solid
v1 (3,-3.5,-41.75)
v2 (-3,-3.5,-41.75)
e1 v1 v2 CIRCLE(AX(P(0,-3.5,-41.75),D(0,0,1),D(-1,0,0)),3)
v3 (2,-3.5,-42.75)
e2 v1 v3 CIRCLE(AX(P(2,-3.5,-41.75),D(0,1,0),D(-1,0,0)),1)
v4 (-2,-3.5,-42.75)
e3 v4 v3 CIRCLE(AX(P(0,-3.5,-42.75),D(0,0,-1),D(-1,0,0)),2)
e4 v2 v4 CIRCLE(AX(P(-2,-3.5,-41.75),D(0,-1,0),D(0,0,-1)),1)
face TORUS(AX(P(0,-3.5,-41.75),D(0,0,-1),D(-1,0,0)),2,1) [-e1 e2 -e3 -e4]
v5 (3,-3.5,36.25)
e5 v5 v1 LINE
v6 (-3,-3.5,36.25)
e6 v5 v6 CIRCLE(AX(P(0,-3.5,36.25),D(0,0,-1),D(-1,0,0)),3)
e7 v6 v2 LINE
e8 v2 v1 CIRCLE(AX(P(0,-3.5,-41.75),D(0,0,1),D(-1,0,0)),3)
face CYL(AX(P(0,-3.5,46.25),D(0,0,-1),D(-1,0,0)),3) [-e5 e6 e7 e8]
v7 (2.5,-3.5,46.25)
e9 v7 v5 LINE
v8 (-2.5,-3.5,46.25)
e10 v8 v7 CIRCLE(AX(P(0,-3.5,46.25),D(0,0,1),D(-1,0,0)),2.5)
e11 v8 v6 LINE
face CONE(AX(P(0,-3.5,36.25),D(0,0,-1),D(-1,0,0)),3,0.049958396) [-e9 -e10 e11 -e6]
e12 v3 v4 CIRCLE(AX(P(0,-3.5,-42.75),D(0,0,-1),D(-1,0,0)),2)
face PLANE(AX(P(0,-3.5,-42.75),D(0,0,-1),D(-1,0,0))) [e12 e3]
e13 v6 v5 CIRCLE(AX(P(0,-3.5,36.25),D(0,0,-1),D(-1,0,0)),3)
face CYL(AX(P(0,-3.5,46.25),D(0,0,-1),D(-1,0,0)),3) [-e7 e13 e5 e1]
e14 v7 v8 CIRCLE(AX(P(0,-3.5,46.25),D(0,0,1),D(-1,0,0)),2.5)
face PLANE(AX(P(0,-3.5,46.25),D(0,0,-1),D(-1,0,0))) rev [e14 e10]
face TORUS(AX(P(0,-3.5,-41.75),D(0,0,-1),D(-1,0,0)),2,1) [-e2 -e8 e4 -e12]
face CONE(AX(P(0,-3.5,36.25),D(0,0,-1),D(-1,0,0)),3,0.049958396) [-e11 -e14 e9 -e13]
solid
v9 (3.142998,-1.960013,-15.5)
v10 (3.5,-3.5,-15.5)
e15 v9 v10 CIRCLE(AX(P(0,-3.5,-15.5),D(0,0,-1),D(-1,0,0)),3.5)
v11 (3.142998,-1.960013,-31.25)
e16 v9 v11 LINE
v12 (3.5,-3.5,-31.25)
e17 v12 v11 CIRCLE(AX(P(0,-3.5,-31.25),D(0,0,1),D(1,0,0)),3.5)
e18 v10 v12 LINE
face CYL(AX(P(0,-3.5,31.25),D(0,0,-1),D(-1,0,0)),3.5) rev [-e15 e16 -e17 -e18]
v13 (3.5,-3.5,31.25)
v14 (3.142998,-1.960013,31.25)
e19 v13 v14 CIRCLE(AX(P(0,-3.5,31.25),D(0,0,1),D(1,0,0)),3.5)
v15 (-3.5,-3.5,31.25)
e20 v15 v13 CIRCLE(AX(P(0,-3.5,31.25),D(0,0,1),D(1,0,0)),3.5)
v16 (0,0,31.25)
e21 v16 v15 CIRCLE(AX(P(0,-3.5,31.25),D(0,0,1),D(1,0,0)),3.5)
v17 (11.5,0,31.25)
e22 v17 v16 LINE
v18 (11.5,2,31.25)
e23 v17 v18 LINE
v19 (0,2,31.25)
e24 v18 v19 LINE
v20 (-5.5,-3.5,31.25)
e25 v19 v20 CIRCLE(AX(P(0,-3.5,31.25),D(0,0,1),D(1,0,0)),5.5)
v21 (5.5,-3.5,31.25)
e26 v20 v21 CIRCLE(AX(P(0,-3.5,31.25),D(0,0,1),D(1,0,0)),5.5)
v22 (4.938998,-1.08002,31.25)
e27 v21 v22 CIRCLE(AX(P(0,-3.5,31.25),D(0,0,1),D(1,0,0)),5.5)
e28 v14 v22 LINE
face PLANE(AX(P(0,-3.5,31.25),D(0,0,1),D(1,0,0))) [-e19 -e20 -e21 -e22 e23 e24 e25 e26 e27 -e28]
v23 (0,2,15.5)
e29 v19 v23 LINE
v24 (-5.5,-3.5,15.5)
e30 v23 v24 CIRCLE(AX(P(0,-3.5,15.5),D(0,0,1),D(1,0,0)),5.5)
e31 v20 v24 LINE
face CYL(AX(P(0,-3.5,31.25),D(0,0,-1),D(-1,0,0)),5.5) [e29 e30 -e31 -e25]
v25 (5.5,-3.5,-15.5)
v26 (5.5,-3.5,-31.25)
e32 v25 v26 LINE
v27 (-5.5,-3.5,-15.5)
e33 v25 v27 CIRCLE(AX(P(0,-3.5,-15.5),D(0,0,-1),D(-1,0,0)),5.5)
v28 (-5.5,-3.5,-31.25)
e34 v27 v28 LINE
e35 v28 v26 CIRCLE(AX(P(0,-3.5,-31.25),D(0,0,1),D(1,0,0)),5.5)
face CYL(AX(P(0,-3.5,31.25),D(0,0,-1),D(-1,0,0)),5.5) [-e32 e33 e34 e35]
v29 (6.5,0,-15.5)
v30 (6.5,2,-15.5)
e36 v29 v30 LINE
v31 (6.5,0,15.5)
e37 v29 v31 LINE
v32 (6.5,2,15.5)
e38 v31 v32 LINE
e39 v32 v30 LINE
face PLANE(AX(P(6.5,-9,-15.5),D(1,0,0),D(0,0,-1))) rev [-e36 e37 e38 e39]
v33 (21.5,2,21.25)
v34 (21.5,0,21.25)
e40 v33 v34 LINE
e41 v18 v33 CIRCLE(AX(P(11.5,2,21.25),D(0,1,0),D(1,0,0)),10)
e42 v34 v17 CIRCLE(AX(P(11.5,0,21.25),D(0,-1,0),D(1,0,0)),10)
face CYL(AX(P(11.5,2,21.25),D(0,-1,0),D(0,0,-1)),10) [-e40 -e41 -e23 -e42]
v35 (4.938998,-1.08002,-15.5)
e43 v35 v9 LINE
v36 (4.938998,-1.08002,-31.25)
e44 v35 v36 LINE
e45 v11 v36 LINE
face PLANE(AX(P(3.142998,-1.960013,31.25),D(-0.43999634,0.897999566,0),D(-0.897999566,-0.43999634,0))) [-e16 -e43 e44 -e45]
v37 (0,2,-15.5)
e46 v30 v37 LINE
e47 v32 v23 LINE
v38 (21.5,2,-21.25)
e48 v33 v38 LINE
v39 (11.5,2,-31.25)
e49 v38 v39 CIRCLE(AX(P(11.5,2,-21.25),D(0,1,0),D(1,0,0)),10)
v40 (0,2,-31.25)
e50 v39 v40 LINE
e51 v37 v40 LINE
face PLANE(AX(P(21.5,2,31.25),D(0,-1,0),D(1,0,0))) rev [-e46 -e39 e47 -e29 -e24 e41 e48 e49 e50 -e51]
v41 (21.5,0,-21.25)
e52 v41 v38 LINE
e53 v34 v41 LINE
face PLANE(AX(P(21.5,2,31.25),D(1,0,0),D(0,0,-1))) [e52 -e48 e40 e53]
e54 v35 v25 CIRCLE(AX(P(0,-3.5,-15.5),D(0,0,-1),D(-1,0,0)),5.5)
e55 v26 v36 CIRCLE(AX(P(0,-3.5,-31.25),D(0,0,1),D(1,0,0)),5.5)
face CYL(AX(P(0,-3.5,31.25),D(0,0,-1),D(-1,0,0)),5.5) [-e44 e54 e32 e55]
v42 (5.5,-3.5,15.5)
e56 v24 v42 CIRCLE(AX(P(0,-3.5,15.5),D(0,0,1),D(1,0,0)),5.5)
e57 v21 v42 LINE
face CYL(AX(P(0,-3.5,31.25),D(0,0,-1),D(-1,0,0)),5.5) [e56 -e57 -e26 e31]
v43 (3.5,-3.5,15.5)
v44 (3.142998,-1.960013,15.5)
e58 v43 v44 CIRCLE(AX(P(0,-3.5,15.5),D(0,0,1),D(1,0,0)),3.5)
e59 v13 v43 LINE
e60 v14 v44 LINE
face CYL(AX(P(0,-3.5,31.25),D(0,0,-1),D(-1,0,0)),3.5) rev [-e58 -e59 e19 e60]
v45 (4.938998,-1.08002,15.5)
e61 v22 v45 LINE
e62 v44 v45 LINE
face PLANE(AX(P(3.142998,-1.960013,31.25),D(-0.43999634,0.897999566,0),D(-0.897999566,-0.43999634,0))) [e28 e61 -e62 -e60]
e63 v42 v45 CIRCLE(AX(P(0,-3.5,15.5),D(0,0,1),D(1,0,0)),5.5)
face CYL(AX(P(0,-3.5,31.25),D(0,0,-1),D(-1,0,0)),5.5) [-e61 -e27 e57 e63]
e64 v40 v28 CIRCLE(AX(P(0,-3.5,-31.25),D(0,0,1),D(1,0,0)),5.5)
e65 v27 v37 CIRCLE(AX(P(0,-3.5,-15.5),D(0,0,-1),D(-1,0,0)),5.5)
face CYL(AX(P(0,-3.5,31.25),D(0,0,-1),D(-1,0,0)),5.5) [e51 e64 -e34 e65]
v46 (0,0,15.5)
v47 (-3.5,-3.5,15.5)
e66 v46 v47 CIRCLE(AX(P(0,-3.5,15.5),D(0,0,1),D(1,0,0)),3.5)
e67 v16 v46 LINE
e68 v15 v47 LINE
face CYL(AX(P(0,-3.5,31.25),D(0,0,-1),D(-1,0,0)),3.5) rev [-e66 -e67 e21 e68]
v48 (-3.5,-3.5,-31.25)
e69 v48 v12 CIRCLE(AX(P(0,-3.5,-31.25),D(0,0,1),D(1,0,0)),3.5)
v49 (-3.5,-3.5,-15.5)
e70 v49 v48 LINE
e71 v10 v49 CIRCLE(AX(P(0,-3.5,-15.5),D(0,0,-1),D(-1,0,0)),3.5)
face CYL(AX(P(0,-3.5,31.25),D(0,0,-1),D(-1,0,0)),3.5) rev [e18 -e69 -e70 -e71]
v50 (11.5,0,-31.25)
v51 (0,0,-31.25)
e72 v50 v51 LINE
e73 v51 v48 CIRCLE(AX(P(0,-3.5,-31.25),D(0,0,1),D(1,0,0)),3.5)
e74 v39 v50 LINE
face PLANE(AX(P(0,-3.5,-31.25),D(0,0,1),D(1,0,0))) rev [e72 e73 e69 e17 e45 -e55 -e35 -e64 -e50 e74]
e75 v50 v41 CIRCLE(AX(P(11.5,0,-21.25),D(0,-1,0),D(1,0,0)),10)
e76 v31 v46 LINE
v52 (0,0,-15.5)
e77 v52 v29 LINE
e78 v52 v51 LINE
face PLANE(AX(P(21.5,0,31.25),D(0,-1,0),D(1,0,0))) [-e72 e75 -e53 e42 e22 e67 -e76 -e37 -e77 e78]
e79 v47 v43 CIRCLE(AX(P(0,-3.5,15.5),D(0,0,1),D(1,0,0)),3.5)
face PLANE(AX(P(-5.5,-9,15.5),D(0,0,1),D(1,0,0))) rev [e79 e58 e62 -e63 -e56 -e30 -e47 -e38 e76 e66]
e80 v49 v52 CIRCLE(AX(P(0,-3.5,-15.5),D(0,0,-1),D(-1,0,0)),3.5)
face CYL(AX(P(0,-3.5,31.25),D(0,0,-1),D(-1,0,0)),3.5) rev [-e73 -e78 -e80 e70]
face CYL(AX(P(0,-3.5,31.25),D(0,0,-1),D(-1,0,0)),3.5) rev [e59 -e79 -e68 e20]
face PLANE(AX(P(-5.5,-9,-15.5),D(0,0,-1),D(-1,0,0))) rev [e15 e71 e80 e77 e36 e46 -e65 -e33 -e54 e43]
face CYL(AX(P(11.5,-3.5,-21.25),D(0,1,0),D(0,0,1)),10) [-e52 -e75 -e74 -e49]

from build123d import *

# Parameters (mm, degrees)
EXTRUDE_5_DEPTH     = 31.25
SKETCH_4_W          = 12
SKETCH_4_H          = 31
CUT_EXTRUDE_1_DEPTH = 40.494461637
SKETCH_8_R          = 3
EXTRUDE_4_DEPTH     = 89
CHAMFER_2_SIZE      = 0.5
CHAMFER_2_SIZE2     = 10
FILLET_1_R          = 10
FILLET_2_R          = 1


with BuildPart() as part:
    # 草图3 → 拉伸-薄壁5 (new, symmetric)
    with BuildSketch(Plane.XY):
        with BuildLine():
            Line((21.5, 0), (0, 0))
            ThreePointArc((0, 0), (-1.852031969, -6.469844707), (3.142998481, -1.960012809))
            Line((3.142998481, -1.960012809), (4.938997613, -1.080020128))
            ThreePointArc((4.938997613, -1.080020128), (-2.910335952, -8.166898826), (0, 2))
            Line((0, 2), (21.5, 2))
            Line((21.5, 2), (21.5, 0))
        make_face()
    extrude(amount=EXTRUDE_5_DEPTH, both=True)

    # 草图4 → 切除-拉伸1 (cut, through all)
    with BuildSketch(Plane(origin=(0, 2, 0), x_dir=(1, 0, 0), z_dir=(0, 1, 0))):
        with Locations((0.5, 0)):
            Rectangle(SKETCH_4_W, SKETCH_4_H)
    extrude(amount=-CUT_EXTRUDE_1_DEPTH, mode=Mode.SUBTRACT)

    # 圆角1
    fillet_1_edges = [part.edges().sort_by_distance(p)[0] for p in [
        (21.5, 1, 31.25),
        (21.5, 1, -31.25),
    ]]
    fillet(fillet_1_edges, radius=FILLET_1_R)


with BuildPart() as body_2:
    # 草图8 → 凸台-拉伸4 (new body)
    with BuildSketch(Plane(origin=(0, 0, -42.75), x_dir=(-1, 0, 0), z_dir=(0, 0, -1))):
        with Locations((0, -3.5)):
            Circle(SKETCH_8_R)
    extrude(amount=-EXTRUDE_4_DEPTH)

    # 倒角2
    chamfer_2_edges = [body_2.edges().sort_by_distance(p)[0] for p in [
        (3, -3.5, 46.25),
    ]]
    chamfer_2_side = [body_2.faces().sort_by_distance(p)[0] for p in [
        (0, -3.5, 46.25),
    ]]
    chamfer(chamfer_2_edges, length=CHAMFER_2_SIZE, length2=CHAMFER_2_SIZE2, reference=chamfer_2_side[0])

    # 圆角2
    fillet_2_edges = [body_2.edges().sort_by_distance(p)[0] for p in [
        (3, -3.5, -42.75),
    ]]
    fillet(fillet_2_edges, radius=FILLET_2_R)


solid = Compound([part.part, body_2.part])
